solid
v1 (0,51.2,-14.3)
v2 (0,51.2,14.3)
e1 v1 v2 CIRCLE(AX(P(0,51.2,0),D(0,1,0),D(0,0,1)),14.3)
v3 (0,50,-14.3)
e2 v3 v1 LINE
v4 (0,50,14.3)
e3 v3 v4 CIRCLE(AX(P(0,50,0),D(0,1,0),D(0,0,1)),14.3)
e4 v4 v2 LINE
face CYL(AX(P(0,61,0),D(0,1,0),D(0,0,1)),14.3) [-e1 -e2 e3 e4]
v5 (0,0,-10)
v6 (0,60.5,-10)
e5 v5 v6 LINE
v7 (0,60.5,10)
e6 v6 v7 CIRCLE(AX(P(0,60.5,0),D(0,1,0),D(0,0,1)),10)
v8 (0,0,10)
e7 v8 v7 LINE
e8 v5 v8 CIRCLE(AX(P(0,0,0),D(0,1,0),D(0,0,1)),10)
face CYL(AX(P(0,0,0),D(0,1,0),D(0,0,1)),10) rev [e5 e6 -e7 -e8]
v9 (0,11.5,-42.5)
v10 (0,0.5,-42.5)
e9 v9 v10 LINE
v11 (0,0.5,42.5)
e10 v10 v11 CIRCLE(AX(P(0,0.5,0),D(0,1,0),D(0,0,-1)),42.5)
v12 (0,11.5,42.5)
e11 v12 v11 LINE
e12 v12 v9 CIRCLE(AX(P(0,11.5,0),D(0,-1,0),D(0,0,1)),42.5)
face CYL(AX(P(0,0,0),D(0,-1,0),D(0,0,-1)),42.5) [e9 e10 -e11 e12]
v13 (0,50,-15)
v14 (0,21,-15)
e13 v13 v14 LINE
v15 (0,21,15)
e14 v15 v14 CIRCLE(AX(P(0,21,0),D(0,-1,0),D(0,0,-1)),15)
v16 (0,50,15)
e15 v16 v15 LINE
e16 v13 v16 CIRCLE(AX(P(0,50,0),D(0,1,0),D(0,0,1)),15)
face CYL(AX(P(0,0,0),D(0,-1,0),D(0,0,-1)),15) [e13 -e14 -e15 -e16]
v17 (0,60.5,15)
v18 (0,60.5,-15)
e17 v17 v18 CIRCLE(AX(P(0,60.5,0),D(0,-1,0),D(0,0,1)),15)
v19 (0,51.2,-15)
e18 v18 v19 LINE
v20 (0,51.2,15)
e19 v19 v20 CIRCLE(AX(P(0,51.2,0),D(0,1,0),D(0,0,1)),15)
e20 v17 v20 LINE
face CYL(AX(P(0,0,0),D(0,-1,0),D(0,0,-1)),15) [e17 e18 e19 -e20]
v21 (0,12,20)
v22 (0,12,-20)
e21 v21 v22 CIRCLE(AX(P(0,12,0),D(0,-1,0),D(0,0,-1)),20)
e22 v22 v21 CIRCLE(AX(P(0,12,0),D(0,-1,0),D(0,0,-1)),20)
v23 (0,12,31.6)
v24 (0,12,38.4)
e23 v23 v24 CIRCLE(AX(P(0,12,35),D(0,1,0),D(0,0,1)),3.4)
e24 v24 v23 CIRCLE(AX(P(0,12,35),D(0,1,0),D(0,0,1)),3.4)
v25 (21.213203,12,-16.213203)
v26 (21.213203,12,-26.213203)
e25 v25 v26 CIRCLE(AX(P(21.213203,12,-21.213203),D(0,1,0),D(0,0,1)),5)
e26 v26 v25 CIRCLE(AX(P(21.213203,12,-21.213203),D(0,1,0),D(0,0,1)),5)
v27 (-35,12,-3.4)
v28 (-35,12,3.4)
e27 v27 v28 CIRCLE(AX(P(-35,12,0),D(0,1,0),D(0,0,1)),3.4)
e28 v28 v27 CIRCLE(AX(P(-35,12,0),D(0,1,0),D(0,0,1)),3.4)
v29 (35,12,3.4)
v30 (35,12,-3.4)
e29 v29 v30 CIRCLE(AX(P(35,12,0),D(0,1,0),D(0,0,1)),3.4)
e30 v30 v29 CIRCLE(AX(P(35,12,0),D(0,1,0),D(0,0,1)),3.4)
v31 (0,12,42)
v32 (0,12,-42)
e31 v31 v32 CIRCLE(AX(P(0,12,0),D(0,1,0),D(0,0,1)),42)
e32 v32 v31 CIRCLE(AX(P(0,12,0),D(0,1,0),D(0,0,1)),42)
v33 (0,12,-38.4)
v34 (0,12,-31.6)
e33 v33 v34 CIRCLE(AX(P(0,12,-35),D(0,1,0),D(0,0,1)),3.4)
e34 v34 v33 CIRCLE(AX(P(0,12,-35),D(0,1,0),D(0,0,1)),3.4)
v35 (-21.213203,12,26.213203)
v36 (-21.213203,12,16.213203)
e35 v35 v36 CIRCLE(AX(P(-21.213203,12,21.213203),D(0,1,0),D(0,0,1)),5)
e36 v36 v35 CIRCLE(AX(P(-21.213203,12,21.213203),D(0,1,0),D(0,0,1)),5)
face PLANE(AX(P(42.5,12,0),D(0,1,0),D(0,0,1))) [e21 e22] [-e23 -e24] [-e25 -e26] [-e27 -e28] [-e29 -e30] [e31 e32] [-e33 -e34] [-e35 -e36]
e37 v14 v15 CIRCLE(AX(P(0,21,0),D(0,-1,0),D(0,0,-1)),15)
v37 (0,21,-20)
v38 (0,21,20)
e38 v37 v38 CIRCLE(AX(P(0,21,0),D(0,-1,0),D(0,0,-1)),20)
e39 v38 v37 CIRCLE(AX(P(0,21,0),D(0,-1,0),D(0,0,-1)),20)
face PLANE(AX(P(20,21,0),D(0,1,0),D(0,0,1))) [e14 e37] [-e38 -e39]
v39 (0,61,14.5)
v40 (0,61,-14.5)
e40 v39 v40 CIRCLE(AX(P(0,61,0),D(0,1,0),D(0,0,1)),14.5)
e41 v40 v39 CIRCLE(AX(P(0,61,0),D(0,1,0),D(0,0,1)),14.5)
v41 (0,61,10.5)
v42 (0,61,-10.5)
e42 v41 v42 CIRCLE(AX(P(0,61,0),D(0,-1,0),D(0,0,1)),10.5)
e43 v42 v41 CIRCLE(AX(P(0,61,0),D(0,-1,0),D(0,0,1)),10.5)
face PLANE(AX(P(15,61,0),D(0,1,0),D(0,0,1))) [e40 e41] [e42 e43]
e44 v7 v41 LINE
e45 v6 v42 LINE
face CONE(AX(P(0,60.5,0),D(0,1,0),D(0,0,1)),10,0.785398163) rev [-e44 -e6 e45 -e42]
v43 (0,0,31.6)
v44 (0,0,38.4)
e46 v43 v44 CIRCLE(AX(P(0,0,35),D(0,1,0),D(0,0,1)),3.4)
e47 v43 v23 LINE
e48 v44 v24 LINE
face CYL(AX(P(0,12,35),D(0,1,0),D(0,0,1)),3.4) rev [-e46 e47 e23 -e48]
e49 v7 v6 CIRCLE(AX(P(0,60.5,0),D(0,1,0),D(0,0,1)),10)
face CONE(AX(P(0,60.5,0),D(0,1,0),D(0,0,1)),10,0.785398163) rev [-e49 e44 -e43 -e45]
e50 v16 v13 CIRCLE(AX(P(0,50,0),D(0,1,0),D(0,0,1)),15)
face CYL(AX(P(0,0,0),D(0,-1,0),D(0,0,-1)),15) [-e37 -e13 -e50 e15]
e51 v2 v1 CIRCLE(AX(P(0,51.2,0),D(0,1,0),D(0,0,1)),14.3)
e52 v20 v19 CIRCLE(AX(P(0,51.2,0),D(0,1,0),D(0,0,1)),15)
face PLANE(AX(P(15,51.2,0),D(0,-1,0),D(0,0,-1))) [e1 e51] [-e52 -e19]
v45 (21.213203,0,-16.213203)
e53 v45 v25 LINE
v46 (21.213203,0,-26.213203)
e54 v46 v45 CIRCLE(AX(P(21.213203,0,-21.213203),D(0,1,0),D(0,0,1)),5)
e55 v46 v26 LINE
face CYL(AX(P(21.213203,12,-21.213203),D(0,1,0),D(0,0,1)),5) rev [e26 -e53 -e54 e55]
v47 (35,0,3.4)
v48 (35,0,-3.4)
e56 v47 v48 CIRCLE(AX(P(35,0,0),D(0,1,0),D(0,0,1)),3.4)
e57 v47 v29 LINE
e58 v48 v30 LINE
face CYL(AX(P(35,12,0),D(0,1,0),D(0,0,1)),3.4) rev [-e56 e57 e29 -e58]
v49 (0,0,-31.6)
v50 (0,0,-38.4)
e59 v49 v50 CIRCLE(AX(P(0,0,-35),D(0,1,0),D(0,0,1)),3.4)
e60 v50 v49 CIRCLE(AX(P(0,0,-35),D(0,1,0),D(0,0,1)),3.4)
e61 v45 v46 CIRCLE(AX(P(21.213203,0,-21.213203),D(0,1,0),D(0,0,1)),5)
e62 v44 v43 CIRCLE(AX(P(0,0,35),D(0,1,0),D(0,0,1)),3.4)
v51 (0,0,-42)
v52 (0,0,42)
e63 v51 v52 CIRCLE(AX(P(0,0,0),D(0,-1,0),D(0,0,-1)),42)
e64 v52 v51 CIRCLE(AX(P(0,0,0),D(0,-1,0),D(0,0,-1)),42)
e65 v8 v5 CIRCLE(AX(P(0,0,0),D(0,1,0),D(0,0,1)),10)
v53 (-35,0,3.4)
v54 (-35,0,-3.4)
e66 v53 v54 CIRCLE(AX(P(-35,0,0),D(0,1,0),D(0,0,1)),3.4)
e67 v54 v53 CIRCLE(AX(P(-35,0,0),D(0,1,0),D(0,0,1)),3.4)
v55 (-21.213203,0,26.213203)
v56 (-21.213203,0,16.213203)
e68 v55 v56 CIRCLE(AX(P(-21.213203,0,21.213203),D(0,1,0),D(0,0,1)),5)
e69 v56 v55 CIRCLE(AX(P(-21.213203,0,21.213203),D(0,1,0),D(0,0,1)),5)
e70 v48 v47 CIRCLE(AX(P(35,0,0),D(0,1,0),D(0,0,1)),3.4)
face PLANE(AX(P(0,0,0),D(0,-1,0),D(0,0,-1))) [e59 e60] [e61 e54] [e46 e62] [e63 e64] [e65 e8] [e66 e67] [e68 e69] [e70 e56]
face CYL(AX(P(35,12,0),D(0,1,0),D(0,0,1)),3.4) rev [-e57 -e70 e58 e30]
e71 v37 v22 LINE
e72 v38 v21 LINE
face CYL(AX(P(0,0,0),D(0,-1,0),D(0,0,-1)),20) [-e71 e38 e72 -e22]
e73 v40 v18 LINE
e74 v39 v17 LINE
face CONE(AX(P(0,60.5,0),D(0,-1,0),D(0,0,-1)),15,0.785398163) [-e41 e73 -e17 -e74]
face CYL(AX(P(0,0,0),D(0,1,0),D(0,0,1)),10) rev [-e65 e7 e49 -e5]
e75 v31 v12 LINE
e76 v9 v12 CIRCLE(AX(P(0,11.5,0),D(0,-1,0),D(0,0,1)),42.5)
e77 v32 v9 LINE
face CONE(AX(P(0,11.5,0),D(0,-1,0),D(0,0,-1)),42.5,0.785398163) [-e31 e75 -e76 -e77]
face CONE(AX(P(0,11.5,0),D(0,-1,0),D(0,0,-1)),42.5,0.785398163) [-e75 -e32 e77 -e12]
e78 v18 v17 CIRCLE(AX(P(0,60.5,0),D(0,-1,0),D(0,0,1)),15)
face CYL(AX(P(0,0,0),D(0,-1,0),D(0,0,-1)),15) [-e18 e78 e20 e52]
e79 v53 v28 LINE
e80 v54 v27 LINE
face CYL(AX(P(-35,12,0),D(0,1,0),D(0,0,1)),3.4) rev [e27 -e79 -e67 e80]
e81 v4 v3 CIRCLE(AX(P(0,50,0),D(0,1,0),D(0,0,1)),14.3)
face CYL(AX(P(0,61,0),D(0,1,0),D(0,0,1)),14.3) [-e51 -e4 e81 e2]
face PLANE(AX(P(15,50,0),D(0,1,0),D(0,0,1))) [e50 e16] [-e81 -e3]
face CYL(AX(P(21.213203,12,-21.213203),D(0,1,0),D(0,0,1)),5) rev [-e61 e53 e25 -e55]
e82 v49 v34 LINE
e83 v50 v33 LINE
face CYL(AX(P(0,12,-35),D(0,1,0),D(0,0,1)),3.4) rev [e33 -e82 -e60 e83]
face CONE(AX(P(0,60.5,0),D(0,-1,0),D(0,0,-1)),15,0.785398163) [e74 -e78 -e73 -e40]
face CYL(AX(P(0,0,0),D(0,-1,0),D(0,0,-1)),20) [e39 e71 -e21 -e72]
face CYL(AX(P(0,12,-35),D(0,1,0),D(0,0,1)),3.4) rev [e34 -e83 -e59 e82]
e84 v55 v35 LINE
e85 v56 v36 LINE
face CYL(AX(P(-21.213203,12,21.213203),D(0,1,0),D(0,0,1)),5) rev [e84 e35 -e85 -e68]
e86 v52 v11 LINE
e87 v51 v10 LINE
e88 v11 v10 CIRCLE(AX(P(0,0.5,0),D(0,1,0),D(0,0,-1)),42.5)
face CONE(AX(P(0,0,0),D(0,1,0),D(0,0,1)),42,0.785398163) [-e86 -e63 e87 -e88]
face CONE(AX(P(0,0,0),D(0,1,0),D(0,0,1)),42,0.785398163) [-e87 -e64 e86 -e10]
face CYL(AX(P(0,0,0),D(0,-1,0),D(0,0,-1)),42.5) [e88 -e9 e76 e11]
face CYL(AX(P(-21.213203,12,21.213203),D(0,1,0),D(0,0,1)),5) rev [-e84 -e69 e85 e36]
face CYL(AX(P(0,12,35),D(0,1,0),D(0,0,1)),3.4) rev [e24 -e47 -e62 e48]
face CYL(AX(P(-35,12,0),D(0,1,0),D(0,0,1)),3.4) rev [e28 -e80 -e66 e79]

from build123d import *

# Parameters (mm, degrees)
SKETCH2_R                  = 10
CUT_EXTRUDE1_DEPTH         = 86.635856976
SKETCH3_W                  = 0.7
SKETCH3_H                  = 1.2
M8_TAPPED_HOLE1_D          = 6.8
F_10_0_10_DIAMETER_HOLE1_D = 10
CHAMFER1_SIZE              = 0.5


with BuildPart() as part:
    # Sketch1 → Revolve1 (revolve)
    with BuildSketch(Plane.XY, mode=Mode.PRIVATE) as revolve1_sk:
        Polygon((0, 0), (42.5, 0), (42.5, 12), (20, 12), (20, 21), (15, 21), (15, 61), (0, 61), align=None)
    revolve(revolve1_sk.sketch.rotate(Axis((0, 0, 0), (0, 1, 0)), 90), axis=Axis((0, 0, 0), (0, 1, 0)))

    # Sketch2 → Cut-Extrude1 (cut, through all)
    with BuildSketch(Plane(origin=(0, 61, 0), x_dir=(1, 0, 0), z_dir=(0, 1, 0))):
        with Locations(Location((0, 0, 0), (0, 0, 270))):
            Circle(SKETCH2_R)
    extrude(amount=-CUT_EXTRUDE1_DEPTH, mode=Mode.SUBTRACT)

    # Sketch3 → Cut-Revolve1 (revolve, cut)
    with BuildSketch(Plane.XY, mode=Mode.PRIVATE) as cut_revolve1_sk:
        with Locations((14.65, 50.6)):
            Rectangle(SKETCH3_W, SKETCH3_H)
    revolve(cut_revolve1_sk.sketch.rotate(Axis((0, 0, 0), (0, -1, 0)), 270), axis=Axis((0, 0, 0), (0, -1, 0)), mode=Mode.SUBTRACT)

    # M8 Tapped Hole1 (through all)
    with Locations(Plane(origin=(0, 12, 0), x_dir=(1, 0, 0), z_dir=(0, 1, 0))):
        with Locations((35, 0), (0, -35), (-35, 0), (0, 35), (0, 0)):
            Hole(M8_TAPPED_HOLE1_D / 2)

    # Ø10.0 (10) Diameter Hole1 (through all)
    with Locations(Plane(origin=(0, 12, 0), x_dir=(1, 0, 0), z_dir=(0, 1, 0))):
        with Locations((-21.213203436, -21.213203436), (21.213203436, 21.213203436)):
            Hole(F_10_0_10_DIAMETER_HOLE1_D / 2)

    # Chamfer1
    chamfer1_edges = [part.edges().sort_by_distance(p)[0] for p in [
        (0, 61, -10),
        (0, 61, 15),
        (0, 12, 42.5),
        (0, 0, 42.5),
    ]]
    chamfer(chamfer1_edges, length=CHAMFER1_SIZE)


solid = part.part
